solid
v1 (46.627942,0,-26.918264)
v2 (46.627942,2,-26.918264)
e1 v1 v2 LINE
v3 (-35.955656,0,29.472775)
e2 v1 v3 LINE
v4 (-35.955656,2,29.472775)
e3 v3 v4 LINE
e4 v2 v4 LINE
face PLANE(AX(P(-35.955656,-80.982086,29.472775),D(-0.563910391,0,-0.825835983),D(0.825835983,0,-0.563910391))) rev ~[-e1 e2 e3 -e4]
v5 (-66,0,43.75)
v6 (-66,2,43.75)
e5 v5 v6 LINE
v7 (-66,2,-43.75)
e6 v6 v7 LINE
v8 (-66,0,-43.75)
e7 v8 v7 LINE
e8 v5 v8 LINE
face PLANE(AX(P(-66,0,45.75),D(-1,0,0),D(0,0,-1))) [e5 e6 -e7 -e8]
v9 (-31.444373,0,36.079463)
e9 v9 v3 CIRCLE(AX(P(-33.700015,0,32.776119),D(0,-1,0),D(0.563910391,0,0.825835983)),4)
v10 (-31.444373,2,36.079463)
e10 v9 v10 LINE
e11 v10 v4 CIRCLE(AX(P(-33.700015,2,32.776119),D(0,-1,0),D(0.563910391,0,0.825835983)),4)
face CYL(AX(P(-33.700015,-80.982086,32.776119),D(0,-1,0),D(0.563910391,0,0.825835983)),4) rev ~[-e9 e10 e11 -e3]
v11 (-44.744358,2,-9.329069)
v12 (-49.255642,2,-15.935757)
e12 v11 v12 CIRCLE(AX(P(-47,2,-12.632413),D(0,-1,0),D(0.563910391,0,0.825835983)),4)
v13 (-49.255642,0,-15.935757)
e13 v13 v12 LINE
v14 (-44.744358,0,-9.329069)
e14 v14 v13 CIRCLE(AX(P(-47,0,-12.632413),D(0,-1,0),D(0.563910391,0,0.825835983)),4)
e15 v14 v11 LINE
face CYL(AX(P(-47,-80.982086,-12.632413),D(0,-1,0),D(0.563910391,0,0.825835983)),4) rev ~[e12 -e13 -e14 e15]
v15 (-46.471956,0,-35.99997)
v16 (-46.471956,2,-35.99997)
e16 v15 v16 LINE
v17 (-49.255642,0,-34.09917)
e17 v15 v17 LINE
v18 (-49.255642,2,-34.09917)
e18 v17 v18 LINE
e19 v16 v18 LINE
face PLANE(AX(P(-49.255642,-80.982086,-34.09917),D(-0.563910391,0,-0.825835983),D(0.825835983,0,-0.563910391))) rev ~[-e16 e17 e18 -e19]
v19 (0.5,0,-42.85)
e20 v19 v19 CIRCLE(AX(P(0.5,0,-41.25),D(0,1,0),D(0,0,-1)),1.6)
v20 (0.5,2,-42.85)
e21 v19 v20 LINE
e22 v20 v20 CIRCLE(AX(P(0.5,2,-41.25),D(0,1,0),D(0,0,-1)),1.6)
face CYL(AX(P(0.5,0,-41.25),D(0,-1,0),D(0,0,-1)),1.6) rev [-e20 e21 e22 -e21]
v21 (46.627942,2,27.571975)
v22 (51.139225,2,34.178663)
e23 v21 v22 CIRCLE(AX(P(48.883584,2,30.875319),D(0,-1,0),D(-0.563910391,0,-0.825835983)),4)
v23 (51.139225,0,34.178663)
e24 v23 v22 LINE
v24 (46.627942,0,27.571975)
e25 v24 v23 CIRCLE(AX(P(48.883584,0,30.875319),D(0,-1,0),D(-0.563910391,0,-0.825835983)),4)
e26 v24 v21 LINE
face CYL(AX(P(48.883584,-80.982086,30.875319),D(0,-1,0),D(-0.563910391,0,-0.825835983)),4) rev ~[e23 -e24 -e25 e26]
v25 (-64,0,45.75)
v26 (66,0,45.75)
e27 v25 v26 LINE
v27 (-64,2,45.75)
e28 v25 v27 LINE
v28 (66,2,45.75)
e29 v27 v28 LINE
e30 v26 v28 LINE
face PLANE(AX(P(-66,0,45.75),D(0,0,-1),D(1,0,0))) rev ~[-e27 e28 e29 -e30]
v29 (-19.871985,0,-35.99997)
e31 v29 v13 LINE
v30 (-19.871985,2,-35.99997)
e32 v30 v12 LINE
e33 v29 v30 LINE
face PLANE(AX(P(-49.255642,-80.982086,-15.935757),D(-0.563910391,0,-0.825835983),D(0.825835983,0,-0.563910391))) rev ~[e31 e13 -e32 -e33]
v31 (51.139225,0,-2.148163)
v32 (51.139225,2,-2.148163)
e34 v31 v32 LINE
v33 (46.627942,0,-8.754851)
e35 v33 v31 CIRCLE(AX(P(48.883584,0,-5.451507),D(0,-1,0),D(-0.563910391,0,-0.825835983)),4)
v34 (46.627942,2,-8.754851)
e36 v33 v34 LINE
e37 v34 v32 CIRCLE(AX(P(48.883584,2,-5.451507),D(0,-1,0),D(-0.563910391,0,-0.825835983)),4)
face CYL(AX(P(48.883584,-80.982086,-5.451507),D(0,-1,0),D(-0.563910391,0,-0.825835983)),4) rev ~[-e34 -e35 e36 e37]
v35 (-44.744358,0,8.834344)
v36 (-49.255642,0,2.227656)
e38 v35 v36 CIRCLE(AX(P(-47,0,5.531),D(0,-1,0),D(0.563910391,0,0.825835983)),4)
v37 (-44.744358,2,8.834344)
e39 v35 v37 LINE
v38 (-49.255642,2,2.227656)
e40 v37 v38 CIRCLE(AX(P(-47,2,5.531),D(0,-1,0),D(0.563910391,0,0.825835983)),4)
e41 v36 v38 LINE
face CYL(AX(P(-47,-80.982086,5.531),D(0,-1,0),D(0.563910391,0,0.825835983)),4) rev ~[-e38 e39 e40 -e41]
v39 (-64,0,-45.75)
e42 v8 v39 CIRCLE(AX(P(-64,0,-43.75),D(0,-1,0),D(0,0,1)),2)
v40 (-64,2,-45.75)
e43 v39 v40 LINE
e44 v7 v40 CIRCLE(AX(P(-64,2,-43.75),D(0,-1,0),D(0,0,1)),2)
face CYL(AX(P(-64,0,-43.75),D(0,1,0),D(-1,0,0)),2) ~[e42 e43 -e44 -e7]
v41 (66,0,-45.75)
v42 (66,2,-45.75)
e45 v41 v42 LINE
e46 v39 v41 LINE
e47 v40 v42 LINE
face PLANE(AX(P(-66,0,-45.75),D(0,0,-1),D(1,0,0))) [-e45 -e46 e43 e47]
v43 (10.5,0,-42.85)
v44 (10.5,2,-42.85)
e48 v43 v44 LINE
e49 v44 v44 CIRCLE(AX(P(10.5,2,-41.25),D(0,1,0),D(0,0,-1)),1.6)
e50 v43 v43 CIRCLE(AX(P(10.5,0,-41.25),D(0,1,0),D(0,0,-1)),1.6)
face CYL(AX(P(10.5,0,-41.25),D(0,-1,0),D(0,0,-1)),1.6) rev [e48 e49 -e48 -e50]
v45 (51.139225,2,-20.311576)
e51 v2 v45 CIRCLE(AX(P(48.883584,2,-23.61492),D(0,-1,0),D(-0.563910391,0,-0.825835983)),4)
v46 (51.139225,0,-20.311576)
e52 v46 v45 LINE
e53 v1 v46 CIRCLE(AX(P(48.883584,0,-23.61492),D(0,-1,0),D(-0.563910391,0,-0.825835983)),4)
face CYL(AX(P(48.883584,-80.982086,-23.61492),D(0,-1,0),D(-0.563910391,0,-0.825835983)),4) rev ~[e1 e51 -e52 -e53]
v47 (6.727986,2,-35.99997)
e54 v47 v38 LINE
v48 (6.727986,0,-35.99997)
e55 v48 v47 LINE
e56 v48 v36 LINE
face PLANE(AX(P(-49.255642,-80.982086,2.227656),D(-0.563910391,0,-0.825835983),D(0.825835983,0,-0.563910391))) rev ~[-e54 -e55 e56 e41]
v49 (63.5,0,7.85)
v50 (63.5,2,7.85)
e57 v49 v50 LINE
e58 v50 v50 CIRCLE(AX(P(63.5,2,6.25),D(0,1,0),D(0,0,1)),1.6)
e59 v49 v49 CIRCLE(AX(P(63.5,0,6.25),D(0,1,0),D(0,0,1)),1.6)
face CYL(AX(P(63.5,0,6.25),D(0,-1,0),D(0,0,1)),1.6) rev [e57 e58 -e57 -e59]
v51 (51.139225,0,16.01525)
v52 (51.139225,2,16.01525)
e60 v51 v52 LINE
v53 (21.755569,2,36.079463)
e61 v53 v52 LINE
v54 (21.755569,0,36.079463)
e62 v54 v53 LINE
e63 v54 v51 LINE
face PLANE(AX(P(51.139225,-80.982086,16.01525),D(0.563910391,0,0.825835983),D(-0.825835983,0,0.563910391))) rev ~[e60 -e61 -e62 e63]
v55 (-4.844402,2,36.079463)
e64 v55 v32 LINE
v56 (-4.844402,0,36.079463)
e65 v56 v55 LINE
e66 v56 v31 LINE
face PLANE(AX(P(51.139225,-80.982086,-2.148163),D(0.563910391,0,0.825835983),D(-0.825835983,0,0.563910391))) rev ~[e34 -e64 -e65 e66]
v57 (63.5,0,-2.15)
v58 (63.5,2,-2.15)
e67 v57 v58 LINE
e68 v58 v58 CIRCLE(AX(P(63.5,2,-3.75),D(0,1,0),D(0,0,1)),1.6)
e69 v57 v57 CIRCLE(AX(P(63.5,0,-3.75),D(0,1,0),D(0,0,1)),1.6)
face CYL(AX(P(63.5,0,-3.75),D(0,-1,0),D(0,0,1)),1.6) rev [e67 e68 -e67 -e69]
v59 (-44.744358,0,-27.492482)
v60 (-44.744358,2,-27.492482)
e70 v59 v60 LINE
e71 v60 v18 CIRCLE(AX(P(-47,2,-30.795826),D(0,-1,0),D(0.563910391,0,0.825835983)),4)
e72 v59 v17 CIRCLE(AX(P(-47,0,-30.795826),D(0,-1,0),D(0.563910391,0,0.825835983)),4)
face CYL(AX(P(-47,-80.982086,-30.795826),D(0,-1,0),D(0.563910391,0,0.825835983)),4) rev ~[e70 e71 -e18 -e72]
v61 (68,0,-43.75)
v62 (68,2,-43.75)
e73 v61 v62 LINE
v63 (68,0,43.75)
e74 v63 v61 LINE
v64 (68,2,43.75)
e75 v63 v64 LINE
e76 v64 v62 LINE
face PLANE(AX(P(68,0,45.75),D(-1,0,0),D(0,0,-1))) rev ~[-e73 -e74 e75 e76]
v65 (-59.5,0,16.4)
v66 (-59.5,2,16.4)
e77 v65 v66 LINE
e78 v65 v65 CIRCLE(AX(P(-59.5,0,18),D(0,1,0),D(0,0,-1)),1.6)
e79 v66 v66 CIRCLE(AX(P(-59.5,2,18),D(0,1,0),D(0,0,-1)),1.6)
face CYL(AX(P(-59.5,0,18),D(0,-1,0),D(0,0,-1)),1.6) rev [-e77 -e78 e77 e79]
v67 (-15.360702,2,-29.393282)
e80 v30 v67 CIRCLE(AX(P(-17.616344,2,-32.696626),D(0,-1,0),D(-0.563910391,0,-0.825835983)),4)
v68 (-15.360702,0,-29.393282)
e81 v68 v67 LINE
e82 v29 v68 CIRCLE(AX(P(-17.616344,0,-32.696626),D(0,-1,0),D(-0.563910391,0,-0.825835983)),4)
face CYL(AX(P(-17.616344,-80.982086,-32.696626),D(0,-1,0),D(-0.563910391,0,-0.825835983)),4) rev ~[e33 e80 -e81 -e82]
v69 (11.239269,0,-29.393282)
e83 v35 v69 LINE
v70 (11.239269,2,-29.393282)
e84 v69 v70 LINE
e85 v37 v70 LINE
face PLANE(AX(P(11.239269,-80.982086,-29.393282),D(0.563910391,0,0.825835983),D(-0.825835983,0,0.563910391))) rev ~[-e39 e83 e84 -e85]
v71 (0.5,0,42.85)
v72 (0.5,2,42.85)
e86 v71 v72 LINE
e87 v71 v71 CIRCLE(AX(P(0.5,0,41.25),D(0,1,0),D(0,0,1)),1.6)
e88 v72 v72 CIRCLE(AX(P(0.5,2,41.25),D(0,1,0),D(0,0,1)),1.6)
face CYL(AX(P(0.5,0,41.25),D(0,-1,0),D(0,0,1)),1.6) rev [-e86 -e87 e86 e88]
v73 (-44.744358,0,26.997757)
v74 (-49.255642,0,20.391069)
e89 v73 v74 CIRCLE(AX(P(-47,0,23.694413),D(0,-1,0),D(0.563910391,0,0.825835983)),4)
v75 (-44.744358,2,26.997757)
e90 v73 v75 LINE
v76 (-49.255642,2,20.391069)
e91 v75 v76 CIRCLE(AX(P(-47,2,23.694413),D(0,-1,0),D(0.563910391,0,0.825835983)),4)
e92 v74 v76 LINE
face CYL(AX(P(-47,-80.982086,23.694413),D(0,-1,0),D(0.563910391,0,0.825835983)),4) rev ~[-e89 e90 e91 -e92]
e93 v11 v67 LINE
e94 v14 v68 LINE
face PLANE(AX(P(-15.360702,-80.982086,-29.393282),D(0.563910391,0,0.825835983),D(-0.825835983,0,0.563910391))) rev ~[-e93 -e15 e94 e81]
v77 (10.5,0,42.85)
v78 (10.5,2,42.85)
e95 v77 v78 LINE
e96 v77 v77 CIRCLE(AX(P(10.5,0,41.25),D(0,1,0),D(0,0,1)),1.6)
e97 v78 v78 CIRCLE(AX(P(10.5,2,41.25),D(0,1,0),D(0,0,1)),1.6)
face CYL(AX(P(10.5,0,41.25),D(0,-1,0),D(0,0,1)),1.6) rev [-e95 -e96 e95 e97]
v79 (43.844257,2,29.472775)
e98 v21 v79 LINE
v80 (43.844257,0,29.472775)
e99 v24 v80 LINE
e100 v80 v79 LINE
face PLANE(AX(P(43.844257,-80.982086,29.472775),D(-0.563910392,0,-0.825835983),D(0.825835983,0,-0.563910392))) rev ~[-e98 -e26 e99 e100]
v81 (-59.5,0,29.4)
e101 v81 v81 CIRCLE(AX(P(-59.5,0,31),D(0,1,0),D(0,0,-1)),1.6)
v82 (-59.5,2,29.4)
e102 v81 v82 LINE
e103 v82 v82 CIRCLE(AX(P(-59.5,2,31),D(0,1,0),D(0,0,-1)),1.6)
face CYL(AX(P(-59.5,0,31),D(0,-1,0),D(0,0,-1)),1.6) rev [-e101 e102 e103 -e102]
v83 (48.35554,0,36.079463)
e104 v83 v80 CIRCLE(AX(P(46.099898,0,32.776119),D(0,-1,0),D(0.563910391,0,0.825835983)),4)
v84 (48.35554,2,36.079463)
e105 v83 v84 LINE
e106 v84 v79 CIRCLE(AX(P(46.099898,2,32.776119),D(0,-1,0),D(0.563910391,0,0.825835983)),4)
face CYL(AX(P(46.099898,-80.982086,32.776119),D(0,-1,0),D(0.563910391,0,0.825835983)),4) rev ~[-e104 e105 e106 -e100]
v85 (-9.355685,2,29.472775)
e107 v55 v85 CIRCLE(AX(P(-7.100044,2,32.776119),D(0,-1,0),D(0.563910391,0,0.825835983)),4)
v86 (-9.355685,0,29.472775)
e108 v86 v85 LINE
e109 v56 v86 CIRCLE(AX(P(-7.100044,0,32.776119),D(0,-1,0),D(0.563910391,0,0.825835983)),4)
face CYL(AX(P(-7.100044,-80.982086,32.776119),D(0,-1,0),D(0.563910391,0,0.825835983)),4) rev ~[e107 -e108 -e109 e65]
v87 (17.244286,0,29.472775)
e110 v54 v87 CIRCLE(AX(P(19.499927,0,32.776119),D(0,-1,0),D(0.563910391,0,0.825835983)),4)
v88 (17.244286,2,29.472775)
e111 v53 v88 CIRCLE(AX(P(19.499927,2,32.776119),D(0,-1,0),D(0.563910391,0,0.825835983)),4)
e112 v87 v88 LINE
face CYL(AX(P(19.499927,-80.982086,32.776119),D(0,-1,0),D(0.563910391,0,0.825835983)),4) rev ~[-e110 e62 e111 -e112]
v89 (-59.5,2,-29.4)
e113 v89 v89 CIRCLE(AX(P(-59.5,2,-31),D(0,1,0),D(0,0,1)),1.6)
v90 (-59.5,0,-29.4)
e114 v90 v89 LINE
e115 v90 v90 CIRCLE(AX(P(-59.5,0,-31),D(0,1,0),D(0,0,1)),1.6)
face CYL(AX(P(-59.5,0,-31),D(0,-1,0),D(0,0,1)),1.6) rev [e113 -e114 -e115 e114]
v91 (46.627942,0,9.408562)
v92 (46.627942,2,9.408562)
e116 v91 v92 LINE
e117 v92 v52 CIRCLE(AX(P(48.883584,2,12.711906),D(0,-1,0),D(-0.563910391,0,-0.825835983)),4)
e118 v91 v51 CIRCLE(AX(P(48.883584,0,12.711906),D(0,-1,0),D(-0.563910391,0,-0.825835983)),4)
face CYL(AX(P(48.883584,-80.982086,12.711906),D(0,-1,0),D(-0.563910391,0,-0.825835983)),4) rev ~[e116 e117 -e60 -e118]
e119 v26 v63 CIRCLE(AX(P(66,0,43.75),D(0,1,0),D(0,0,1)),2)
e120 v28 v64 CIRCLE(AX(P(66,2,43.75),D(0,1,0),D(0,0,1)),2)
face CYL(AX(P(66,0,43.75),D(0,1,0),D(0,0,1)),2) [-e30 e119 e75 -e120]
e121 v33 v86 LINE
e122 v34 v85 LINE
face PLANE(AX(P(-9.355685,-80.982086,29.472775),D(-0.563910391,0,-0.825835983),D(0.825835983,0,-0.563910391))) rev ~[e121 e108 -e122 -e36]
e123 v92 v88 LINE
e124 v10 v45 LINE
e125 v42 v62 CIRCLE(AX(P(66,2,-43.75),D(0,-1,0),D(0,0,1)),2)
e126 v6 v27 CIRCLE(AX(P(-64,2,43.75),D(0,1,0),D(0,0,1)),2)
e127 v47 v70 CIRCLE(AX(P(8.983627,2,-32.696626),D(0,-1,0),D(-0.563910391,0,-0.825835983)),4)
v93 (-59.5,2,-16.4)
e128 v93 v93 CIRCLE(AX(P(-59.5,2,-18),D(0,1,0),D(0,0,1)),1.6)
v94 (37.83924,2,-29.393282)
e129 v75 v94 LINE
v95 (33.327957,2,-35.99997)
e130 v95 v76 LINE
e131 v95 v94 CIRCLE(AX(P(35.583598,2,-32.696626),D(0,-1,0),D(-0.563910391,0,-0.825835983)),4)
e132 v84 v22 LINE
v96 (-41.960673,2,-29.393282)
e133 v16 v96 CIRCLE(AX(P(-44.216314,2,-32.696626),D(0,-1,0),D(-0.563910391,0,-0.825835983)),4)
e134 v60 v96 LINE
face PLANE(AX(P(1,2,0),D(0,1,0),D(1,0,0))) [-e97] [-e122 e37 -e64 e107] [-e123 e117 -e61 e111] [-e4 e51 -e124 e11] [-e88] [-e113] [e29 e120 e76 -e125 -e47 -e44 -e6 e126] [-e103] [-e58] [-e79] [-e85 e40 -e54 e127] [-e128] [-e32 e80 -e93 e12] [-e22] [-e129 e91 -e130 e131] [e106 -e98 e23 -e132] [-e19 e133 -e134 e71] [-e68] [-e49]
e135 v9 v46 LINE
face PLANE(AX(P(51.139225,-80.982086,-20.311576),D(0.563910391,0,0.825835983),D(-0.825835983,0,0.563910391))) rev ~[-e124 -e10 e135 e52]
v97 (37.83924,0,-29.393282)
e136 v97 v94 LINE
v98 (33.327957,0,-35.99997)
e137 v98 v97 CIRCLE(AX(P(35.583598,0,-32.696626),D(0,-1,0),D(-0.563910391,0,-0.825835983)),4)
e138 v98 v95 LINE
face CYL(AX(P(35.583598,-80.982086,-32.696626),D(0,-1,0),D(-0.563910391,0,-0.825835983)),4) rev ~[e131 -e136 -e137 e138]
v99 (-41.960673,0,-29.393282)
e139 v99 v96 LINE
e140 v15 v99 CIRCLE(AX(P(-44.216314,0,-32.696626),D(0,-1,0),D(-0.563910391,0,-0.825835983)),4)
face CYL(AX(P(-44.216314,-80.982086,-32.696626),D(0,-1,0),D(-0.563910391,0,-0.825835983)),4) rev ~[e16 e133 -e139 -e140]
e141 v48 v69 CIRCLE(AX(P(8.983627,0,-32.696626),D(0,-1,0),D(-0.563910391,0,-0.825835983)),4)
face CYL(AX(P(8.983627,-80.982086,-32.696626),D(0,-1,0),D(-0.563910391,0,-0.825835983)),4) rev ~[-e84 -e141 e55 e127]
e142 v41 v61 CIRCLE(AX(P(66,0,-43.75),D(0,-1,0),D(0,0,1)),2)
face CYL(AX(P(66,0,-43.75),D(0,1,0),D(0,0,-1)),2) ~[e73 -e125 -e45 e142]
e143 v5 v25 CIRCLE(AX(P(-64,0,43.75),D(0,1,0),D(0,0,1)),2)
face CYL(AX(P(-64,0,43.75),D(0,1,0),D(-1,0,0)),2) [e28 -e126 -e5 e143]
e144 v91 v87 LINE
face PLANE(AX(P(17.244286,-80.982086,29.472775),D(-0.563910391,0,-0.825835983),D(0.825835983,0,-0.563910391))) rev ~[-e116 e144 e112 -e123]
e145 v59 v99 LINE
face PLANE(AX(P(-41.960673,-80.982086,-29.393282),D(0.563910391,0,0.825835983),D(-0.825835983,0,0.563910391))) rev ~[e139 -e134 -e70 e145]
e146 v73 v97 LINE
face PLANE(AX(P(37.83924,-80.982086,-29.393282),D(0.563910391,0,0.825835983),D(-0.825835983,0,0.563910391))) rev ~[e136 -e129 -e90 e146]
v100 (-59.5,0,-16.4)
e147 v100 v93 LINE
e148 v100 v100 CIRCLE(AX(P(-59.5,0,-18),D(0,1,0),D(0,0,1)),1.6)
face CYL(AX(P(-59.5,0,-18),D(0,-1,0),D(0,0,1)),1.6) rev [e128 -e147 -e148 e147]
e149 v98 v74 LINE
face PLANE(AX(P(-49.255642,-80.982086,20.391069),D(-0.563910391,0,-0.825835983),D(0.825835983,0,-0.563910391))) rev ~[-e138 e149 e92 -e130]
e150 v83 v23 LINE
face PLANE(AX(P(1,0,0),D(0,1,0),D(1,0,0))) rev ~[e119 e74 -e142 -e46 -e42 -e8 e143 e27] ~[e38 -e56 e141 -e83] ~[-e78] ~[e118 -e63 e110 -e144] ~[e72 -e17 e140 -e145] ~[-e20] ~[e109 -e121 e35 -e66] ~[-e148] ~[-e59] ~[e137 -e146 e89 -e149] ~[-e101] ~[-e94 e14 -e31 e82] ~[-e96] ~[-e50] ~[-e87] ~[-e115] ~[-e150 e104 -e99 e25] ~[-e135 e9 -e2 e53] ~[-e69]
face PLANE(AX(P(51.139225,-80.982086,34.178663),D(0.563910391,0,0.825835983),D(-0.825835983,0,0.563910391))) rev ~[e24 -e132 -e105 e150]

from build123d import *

# Parameters (mm, degrees)
SKETCH_1_W               = 134
SKETCH_1_H               = 91.5
SKETCH_1_R               = 1.6
EXTRUDE_1_DEPTH          = 2
CUT_EXTRUDE_2_DEPTH      = 82.982086458
CUT_EXTRUDE_2_DEPTH_BACK = 82.982086458
FILLET_R2_1_R            = 2


with BuildPart() as part:
    # 草图1 → 凸台-拉伸1 (new body)
    with BuildSketch(Plane(origin=(0, 0, 0), x_dir=(1, 0, 0), z_dir=(0, 1, 0))):
        with Locations((1, 0)):
            Rectangle(SKETCH_1_W, SKETCH_1_H)
        with Locations(Location((-59.5, 31, 0), (0, 0, 270))):
            Circle(SKETCH_1_R, mode=Mode.SUBTRACT)
        with Locations(Location((-59.5, 18, 0), (0, 0, 270))):
            Circle(SKETCH_1_R, mode=Mode.SUBTRACT)
        with Locations(Location((-59.5, -18, 0), (0, 0, 90))):
            Circle(SKETCH_1_R, mode=Mode.SUBTRACT)
        with Locations(Location((-59.5, -31, 0), (0, 0, 90))):
            Circle(SKETCH_1_R, mode=Mode.SUBTRACT)
        with Locations(Location((63.5, 3.75, 0), (0, 0, 270))):
            Circle(SKETCH_1_R, mode=Mode.SUBTRACT)
        with Locations(Location((63.5, -6.25, 0), (0, 0, 270))):
            Circle(SKETCH_1_R, mode=Mode.SUBTRACT)
        with Locations(Location((0.5, -41.25, 0), (0, 0, 270))):
            Circle(SKETCH_1_R, mode=Mode.SUBTRACT)
        with Locations(Location((10.5, -41.25, 0), (0, 0, 270))):
            Circle(SKETCH_1_R, mode=Mode.SUBTRACT)
        with Locations(Location((10.5, 41.25, 0), (0, 0, 90))):
            Circle(SKETCH_1_R, mode=Mode.SUBTRACT)
        with Locations(Location((0.5, 41.25, 0), (0, 0, 90))):
            Circle(SKETCH_1_R, mode=Mode.SUBTRACT)
    extrude(amount=EXTRUDE_1_DEPTH)

    # 草图5 → 切除-拉伸2 (cut, two sides: drawn at the far end of the back side and taken through both)
    with BuildSketch(Plane(origin=(0, 2, 0), x_dir=(1, 0, 0), z_dir=(0, 1, 0)).offset(-CUT_EXTRUDE_2_DEPTH_BACK)):
        with BuildLine():
            Line((-49.255641565, 34.099169914), (-46.471955987, 35.999970141))
            ThreePointArc((-46.471955987, 35.999970141), (-40.91297049, 34.952267774), (-41.960672856, 29.393282278))
            Line((-41.960672856, 29.393282278), (-44.744358435, 27.492482051))
            ThreePointArc((-44.744358435, 27.492482051), (-50.303343931, 28.540184417), (-49.255641565, 34.099169914))
        make_face()
        with BuildLine():
            Line((-49.255641565, 15.935756946), (-19.871985084, 35.999970141))
            ThreePointArc((-19.871985084, 35.999970141), (-14.312999587, 34.952267774), (-15.360701954, 29.393282278))
            Line((-15.360701954, 29.393282278), (-44.744358435, 9.329069084))
            ThreePointArc((-44.744358435, 9.329069084), (-50.303343931, 10.37677145), (-49.255641565, 15.935756946))
        make_face()
        with BuildLine():
            Line((-49.255641565, -2.227656021), (6.727985819, 35.999970141))
            ThreePointArc((6.727985819, 35.999970141), (12.286971315, 34.952267774), (11.239268949, 29.393282278))
            Line((11.239268949, 29.393282278), (-44.744358435, -8.834343884))
            ThreePointArc((-44.744358435, -8.834343884), (-50.303343931, -7.786641517), (-49.255641565, -2.227656021))
        make_face()
        with BuildLine():
            Line((-49.255641565, -20.391068988), (33.327956722, 35.999970141))
            ThreePointArc((33.327956722, 35.999970141), (38.886942218, 34.952267774), (37.839239852, 29.393282278))
            Line((37.839239852, 29.393282278), (-44.744358435, -26.997756851))
            ThreePointArc((-44.744358435, -26.997756851), (-50.303343931, -25.950054485), (-49.255641565, -20.391068988))
        make_face()
        with BuildLine():
            Line((-35.955656114, -29.472775472), (46.627942173, 26.918263657))
            ThreePointArc((46.627942173, 26.918263657), (52.18692767, 25.870561291), (51.139225303, 20.311575794))
            Line((51.139225303, 20.311575794), (-31.444372983, -36.079463334))
            ThreePointArc((-31.444372983, -36.079463334), (-37.00335848, -35.031760968), (-35.955656114, -29.472775472))
        make_face()
        with BuildLine():
            Line((-9.355685211, -29.472775472), (46.627942173, 8.75485069))
            ThreePointArc((46.627942173, 8.75485069), (52.18692767, 7.707148324), (51.139225303, 2.148162827))
            Line((51.139225303, 2.148162827), (-4.844402081, -36.079463334))
            ThreePointArc((-4.844402081, -36.079463334), (-10.403387577, -35.031760968), (-9.355685211, -29.472775472))
        make_face()
        with BuildLine():
            Line((17.244285692, -29.472775472), (46.627942173, -9.408562277))
            ThreePointArc((46.627942173, -9.408562277), (52.18692767, -10.456264644), (51.139225303, -16.01525014))
            Line((51.139225303, -16.01525014), (21.755568822, -36.079463334))
            ThreePointArc((21.755568822, -36.079463334), (16.196583325, -35.031760968), (17.244285692, -29.472775472))
        make_face()
        with BuildLine():
            Line((43.844256595, -29.472775472), (46.627942173, -27.571975244))
            ThreePointArc((46.627942173, -27.571975244), (52.18692767, -28.619677611), (51.139225303, -34.178663107))
            Line((51.139225303, -34.178663107), (48.355539725, -36.079463334))
            ThreePointArc((48.355539725, -36.079463334), (42.796554228, -35.031760968), (43.844256595, -29.472775472))
        make_face()
    extrude(amount=CUT_EXTRUDE_2_DEPTH + CUT_EXTRUDE_2_DEPTH_BACK, mode=Mode.SUBTRACT)

    # R2 圆角1
    fillet_r2_1_edges = [part.edges().sort_by_distance(p)[0] for p in [
        (-66, 1, -45.75),
        (68, 1, -45.75),
        (68, 1, 45.75),
        (-66, 1, 45.75),
    ]]
    fillet(fillet_r2_1_edges, radius=FILLET_R2_1_R)


solid = part.part
